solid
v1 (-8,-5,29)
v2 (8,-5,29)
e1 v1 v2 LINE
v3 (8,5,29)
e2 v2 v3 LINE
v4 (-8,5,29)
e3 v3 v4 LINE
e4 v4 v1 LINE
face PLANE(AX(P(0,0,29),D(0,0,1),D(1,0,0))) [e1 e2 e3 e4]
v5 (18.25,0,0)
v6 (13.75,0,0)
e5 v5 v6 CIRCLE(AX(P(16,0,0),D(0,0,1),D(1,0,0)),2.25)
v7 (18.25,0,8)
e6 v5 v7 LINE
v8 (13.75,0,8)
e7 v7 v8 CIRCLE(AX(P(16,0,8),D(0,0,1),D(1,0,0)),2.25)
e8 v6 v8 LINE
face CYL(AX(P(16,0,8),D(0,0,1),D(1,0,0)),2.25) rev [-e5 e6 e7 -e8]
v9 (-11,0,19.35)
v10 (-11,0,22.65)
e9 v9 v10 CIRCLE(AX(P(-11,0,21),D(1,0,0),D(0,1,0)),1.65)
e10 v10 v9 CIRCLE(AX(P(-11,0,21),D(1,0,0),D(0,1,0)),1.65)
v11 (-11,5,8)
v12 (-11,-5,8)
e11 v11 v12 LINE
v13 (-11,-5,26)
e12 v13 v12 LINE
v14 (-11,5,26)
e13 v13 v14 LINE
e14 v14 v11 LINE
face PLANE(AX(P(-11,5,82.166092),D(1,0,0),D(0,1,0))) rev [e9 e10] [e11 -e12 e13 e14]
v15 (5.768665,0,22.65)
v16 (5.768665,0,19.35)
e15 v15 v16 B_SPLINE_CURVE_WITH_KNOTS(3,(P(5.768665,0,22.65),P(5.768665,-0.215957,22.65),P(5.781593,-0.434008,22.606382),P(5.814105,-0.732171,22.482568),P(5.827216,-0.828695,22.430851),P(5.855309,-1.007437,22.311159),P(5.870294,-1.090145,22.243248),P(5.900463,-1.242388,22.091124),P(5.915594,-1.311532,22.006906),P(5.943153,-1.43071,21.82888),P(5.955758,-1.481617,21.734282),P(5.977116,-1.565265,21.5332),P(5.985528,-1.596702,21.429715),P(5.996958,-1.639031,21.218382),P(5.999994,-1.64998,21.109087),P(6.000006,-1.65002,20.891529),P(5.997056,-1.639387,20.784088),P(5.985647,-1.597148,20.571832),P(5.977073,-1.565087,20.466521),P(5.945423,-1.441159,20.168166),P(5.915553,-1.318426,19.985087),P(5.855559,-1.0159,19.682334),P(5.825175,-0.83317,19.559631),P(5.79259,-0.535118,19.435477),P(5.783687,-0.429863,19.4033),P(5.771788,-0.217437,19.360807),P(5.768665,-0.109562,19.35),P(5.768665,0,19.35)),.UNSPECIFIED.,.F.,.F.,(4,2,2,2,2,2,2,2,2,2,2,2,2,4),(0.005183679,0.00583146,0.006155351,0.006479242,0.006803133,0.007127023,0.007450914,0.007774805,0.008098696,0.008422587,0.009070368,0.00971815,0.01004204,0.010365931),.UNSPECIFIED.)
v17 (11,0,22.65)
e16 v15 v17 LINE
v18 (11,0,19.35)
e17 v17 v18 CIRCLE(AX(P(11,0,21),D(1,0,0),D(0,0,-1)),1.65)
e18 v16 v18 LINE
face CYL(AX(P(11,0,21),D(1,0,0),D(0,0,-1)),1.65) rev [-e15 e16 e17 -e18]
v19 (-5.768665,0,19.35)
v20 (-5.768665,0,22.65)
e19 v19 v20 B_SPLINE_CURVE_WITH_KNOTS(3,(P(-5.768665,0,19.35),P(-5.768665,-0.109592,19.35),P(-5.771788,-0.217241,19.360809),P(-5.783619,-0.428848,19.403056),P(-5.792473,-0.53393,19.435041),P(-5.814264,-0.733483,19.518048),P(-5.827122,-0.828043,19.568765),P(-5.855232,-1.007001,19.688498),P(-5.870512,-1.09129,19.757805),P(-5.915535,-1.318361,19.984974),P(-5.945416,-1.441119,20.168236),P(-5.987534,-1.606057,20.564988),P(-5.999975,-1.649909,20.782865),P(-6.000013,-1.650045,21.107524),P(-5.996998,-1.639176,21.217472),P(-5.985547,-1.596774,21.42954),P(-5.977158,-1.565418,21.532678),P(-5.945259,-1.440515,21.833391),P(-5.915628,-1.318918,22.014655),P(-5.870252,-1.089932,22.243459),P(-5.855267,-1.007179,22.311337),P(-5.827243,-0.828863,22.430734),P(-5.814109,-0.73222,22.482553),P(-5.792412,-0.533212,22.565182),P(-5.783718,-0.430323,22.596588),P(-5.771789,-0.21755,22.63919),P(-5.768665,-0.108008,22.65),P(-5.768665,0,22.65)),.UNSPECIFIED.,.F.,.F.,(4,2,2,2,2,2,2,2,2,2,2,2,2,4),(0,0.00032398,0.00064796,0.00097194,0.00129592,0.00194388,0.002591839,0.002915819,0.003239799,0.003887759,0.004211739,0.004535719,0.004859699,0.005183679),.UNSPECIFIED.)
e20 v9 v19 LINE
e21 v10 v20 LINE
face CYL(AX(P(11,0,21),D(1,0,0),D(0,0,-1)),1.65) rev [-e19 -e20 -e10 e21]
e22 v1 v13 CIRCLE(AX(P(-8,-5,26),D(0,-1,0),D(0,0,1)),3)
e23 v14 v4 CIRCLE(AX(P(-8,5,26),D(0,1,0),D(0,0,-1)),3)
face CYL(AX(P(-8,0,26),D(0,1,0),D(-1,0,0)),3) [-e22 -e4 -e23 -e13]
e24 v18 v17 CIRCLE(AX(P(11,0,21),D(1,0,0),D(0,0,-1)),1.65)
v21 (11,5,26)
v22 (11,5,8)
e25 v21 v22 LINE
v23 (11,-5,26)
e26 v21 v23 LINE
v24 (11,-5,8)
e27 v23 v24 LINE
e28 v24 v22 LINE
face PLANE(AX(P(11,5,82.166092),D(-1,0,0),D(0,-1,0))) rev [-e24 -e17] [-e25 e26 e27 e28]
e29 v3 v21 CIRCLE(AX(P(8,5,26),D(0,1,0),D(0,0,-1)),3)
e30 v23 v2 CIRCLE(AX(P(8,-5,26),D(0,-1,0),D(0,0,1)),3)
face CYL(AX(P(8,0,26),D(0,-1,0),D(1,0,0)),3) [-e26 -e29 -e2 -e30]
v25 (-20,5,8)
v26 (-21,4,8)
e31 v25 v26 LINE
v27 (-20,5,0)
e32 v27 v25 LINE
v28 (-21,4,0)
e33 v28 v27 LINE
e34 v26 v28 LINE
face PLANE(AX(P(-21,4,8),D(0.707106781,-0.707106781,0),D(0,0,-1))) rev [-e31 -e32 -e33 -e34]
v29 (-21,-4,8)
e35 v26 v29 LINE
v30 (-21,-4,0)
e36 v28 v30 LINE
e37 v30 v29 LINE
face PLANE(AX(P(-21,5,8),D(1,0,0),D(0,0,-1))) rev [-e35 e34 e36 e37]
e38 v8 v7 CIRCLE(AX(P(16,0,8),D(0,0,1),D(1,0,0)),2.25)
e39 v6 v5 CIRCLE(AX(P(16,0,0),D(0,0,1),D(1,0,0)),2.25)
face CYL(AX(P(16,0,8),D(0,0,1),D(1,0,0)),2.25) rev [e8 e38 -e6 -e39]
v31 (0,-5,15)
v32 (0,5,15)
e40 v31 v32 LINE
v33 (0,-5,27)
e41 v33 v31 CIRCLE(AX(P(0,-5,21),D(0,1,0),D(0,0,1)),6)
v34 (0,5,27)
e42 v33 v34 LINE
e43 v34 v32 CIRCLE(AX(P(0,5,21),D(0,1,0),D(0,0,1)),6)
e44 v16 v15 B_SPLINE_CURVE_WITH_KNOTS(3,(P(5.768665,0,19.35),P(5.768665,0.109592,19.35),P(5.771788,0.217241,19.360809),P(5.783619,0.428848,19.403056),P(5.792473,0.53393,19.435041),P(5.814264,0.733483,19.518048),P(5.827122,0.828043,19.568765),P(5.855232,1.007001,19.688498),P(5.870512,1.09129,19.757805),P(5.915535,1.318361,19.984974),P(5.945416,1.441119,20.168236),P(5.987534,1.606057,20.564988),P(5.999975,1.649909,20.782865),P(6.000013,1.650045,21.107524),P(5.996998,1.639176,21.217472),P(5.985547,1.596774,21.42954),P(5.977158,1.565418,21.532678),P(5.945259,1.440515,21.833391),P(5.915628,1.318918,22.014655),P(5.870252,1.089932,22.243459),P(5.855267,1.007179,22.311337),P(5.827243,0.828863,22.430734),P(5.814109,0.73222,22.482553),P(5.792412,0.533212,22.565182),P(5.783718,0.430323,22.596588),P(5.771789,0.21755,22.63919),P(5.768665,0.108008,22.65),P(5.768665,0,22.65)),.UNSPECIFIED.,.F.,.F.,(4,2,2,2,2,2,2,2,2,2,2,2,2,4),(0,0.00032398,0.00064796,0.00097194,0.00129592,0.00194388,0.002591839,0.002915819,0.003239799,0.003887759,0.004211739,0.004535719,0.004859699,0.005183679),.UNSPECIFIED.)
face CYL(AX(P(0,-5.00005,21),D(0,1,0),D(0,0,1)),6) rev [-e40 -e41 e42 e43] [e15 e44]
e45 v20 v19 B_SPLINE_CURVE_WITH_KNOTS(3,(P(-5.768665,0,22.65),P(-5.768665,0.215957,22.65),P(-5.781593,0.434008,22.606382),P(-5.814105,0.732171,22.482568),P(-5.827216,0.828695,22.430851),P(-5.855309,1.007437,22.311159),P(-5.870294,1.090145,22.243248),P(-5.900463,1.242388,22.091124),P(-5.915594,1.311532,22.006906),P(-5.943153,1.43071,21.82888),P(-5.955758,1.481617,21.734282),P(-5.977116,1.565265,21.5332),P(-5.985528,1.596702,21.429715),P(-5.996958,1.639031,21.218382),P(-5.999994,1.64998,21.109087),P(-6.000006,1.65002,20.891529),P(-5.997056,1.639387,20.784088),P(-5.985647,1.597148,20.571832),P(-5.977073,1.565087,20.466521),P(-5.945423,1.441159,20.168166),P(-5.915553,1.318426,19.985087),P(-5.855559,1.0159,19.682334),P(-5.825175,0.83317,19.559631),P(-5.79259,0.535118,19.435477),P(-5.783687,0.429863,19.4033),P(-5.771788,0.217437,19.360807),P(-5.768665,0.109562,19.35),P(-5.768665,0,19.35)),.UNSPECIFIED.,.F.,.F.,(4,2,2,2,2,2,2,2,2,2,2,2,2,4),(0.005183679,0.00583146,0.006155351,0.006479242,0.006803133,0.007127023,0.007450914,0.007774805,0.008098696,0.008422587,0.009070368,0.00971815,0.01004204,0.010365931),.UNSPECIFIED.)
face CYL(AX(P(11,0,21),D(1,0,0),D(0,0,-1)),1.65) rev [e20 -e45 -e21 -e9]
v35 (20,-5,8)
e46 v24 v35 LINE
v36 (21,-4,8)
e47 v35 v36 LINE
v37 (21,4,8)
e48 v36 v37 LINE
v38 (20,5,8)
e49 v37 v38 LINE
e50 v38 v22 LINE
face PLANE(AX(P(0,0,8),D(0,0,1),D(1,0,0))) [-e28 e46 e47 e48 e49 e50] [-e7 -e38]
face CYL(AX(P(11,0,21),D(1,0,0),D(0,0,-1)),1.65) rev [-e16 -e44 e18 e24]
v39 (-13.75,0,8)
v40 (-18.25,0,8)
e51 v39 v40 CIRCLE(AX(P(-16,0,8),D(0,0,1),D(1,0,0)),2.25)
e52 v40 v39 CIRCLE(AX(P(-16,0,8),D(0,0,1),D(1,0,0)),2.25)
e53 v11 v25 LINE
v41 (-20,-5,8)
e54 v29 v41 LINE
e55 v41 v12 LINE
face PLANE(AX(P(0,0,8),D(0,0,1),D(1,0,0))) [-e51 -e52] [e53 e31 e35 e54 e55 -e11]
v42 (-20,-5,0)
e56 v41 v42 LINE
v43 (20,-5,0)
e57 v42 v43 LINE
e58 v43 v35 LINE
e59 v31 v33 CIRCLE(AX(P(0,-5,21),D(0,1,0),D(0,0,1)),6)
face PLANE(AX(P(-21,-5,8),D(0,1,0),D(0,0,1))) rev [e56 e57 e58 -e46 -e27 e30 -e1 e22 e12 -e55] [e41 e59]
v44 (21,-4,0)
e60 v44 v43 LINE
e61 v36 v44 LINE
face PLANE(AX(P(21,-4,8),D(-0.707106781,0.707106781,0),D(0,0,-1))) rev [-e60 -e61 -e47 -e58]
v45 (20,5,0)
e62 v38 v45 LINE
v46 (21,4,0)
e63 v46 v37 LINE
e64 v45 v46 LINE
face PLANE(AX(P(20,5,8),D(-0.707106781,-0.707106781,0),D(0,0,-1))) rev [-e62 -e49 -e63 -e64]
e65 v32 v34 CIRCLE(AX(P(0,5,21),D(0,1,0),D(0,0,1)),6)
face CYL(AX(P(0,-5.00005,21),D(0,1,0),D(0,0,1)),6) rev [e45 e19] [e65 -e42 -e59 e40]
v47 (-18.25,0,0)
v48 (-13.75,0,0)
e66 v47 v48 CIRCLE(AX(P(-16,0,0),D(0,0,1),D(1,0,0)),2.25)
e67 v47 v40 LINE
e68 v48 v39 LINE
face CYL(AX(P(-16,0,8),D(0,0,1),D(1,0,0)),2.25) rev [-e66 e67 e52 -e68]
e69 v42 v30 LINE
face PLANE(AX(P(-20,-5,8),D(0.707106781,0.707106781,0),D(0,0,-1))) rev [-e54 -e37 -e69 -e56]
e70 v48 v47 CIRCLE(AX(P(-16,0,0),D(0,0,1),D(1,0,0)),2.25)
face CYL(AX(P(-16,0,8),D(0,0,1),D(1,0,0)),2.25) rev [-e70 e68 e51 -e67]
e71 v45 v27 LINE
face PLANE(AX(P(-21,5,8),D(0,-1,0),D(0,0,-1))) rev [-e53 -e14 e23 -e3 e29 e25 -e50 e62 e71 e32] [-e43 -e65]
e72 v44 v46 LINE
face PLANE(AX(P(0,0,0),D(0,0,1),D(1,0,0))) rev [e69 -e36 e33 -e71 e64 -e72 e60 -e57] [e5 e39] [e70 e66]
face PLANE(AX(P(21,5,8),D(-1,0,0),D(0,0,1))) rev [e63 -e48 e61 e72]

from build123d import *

# Parameters (mm, degrees)
SKETCH_1_W              = 42
SKETCH_1_H              = 10
EXTRUDE_1_DEPTH         = 8
SKETCH_2_W              = 22
SKETCH_2_H              = 10
EXTRUDE_2_DEPTH         = 21
SKETCH_3_R              = 6
CUT_EXTRUDE_1_DEPTH     = 38.175260591
HOLE_WIZARD_4_5_4_5_2_D = 4.5
HOLE_WIZARD_M4_1_D      = 3.3
FILLET_3_R              = 3
CHAMFER_1_SIZE          = 1


with BuildPart() as part:
    # 草图1 → 凸台-拉伸1 (new body)
    with BuildSketch(Plane.XY):
        Rectangle(SKETCH_1_W, SKETCH_1_H)
    extrude(amount=EXTRUDE_1_DEPTH)

    # 草图2 → 凸台-拉伸2 (add)
    with BuildSketch(Plane.XY.offset(8)):
        Rectangle(SKETCH_2_W, SKETCH_2_H)
    extrude(amount=EXTRUDE_2_DEPTH)

    # 草图3 → 切除-拉伸1 (cut, through all)
    with BuildSketch(Plane(origin=(0, 5, 0), x_dir=(1, 0, 0), z_dir=(0, 1, 0))):
        with Locations(Location((0, -21, 0), (0, 0, 270))):
            Circle(SKETCH_3_R)
    extrude(amount=-CUT_EXTRUDE_1_DEPTH, mode=Mode.SUBTRACT)

    # Ø4.5 (4.5) 直径孔2 (through all)
    with Locations(Plane.XY.offset(8)):
        with Locations((-16, 0), (16, 0)):
            Hole(HOLE_WIZARD_4_5_4_5_2_D / 2)

    # M4 螺纹孔1 (through all)
    with Locations(Plane(origin=(11, 0, 0), x_dir=(0, 0, -1), z_dir=(1, 0, 0))):
        with Locations((-21, 0)):
            Hole(HOLE_WIZARD_M4_1_D / 2)

    # 圆角3
    fillet_3_edges = [part.edges().sort_by_distance(p)[0] for p in [
        (-11, 0, 29),
        (11, 0, 29),
    ]]
    fillet(fillet_3_edges, radius=FILLET_3_R)

    # 倒角1
    chamfer_1_edges = [part.edges().sort_by_distance(p)[0] for p in [
        (21, -5, 4),
        (21, 5, 4),
        (-21, -5, 4),
        (-21, 5, 4),
    ]]
    chamfer(chamfer_1_edges, length=CHAMFER_1_SIZE)


solid = part.part
